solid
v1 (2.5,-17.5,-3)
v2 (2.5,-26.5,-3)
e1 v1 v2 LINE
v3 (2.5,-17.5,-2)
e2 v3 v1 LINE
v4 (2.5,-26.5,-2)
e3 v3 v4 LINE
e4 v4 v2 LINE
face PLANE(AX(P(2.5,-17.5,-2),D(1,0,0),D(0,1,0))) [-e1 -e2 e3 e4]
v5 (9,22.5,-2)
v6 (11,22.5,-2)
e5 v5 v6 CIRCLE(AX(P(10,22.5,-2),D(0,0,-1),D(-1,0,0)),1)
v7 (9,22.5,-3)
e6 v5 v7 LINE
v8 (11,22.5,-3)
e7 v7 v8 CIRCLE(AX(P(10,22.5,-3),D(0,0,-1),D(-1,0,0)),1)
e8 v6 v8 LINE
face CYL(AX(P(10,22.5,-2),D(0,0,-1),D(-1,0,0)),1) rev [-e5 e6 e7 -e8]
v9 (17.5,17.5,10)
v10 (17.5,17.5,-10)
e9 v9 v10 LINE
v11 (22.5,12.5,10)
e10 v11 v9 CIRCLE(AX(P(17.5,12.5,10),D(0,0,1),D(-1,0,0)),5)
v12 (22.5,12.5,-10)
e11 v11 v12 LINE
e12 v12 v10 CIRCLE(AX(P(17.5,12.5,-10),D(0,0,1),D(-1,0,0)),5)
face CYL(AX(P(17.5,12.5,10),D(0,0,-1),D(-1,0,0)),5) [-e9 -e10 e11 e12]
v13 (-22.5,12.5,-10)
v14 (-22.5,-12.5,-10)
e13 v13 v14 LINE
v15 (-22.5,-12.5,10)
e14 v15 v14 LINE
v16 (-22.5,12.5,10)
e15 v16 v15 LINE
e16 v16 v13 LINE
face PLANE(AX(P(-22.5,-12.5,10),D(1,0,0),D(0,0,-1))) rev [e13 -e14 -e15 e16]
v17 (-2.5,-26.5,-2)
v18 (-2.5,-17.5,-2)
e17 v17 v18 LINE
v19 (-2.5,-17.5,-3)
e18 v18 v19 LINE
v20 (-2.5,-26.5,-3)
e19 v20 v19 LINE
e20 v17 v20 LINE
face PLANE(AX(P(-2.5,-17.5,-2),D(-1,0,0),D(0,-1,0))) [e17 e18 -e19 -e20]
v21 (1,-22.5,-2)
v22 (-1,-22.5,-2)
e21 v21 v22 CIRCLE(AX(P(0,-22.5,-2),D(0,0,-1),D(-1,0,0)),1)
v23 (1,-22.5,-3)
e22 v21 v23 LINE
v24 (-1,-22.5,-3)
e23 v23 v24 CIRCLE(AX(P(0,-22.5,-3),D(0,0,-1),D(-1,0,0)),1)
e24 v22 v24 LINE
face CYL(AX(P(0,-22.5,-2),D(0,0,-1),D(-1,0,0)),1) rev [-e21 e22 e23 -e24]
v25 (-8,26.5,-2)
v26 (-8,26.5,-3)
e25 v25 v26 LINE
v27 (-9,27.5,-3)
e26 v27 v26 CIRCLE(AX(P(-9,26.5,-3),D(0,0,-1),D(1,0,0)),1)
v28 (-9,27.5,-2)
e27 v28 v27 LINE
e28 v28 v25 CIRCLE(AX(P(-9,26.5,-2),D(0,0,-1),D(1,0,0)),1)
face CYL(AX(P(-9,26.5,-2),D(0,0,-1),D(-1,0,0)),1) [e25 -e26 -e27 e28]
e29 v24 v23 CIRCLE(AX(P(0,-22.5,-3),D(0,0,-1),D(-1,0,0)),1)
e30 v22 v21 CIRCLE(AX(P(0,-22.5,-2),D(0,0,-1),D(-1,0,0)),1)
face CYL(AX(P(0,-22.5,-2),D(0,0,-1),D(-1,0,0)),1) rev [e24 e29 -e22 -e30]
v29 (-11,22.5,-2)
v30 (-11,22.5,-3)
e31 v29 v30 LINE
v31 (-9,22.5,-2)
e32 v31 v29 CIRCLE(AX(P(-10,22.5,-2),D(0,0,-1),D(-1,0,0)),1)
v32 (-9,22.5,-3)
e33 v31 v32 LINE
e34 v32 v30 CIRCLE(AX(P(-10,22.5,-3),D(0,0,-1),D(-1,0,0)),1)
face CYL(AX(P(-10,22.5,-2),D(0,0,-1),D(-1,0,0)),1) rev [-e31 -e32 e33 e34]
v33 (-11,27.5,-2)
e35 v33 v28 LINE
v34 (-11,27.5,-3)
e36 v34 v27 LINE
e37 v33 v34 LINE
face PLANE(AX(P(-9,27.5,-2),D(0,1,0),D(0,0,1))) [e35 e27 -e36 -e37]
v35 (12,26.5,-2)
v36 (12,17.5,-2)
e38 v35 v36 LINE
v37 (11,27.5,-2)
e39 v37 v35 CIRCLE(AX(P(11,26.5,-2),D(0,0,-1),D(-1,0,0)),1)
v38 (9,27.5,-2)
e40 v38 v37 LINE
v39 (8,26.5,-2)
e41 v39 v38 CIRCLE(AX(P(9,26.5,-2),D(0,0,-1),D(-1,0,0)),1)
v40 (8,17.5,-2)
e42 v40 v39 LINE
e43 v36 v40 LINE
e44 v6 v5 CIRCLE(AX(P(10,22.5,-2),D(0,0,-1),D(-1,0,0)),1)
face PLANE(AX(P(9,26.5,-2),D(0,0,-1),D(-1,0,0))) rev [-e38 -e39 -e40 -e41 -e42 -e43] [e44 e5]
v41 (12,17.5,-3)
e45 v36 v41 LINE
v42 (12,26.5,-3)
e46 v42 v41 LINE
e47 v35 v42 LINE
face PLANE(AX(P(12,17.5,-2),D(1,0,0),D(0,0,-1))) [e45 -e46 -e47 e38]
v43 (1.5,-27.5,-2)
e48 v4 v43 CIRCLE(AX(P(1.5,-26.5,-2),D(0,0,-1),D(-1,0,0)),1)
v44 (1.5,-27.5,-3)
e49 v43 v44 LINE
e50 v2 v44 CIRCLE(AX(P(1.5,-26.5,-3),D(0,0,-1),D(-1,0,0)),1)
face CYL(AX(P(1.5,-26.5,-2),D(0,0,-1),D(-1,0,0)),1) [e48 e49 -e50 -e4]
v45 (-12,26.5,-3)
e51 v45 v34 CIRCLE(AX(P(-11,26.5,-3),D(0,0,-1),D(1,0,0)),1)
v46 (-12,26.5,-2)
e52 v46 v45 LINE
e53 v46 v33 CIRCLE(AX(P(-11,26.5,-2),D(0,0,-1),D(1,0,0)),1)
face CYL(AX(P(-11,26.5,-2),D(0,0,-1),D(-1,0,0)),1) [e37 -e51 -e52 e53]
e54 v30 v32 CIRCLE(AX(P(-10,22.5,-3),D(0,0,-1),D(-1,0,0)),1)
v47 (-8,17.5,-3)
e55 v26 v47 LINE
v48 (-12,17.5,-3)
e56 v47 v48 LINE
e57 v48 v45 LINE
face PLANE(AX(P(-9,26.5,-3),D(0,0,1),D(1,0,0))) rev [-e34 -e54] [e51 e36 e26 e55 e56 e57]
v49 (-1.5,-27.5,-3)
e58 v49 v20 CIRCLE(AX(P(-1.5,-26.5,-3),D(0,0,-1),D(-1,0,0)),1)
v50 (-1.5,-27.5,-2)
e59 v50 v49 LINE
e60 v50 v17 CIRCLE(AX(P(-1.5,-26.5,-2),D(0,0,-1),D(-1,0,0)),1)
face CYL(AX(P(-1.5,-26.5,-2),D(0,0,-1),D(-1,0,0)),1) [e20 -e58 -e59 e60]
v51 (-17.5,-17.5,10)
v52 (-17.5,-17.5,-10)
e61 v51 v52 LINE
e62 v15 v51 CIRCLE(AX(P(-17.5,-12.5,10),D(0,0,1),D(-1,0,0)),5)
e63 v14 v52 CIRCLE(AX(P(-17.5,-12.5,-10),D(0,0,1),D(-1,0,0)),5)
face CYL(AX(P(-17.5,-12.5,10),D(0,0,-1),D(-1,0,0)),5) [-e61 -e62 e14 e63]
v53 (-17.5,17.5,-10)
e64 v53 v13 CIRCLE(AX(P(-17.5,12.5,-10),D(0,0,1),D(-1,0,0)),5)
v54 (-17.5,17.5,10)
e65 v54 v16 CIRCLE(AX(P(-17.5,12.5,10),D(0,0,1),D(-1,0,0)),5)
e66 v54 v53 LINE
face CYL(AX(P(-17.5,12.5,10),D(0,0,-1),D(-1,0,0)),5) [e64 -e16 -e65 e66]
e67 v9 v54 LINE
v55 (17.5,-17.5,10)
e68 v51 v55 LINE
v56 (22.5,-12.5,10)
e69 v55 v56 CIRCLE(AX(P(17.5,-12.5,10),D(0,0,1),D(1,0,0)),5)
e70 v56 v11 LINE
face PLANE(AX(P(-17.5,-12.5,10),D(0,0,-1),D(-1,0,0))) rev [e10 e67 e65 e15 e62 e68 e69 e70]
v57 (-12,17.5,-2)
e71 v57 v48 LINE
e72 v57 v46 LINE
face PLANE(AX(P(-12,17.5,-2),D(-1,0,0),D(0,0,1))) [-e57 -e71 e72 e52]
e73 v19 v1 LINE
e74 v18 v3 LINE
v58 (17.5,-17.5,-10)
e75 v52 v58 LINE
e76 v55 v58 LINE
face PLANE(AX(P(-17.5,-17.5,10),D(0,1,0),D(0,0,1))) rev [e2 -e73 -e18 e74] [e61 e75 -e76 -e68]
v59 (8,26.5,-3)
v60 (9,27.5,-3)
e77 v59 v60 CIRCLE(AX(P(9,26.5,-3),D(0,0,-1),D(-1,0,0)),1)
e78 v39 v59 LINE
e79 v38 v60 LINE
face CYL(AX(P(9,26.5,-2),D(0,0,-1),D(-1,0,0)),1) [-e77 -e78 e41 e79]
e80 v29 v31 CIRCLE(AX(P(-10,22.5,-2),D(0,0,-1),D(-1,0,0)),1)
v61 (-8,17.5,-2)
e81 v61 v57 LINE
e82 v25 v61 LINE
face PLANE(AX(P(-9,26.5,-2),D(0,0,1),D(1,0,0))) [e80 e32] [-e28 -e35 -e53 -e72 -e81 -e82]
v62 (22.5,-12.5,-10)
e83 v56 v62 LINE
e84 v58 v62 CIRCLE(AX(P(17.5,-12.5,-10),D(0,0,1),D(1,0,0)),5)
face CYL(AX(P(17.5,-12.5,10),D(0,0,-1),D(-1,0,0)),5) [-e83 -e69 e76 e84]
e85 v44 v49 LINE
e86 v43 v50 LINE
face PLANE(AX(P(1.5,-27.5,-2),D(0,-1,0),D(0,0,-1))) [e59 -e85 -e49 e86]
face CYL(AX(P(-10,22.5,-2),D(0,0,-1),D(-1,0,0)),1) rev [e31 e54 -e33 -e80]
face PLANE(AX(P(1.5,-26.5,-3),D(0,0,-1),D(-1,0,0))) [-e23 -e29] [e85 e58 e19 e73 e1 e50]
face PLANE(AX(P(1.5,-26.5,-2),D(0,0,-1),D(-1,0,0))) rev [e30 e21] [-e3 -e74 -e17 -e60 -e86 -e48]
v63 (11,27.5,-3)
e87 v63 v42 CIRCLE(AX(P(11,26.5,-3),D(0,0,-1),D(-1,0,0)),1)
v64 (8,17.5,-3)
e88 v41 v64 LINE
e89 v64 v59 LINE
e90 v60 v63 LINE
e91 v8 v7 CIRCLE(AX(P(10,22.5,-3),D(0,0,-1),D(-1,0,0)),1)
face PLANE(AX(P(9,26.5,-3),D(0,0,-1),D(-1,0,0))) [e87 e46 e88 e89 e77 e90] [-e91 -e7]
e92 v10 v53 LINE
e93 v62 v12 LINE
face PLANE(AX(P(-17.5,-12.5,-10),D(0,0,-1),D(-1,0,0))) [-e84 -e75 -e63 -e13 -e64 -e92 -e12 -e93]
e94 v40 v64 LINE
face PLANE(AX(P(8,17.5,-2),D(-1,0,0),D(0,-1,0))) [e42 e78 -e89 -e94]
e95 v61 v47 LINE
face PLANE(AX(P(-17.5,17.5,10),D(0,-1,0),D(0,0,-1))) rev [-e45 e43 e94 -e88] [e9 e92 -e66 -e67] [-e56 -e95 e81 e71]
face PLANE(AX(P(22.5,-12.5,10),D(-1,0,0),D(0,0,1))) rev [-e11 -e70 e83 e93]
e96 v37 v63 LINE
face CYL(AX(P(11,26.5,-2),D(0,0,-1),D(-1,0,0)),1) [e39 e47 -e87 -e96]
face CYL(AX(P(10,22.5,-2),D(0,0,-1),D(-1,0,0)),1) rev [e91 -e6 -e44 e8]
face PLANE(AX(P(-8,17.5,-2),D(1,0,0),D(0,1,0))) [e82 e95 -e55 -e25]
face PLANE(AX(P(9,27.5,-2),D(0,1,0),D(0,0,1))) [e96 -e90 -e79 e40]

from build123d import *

# Parameters (mm, degrees)
BOSS_EXTRUDE1_DEPTH = 10
SKETCH3_R           = 1
BOSS_EXTRUDE2_DEPTH = 1
SKETCH4_R           = 1
CUT_EXTRUDE1_DEPTH  = 1


with BuildPart() as part:
    # Sketch1 → Boss-Extrude1 (new, symmetric)
    with BuildSketch(Plane.XY):
        with BuildLine():
            Line((-17.5, -17.5), (17.5, -17.5))
            ThreePointArc((17.5, -17.5), (21.035533906, -16.035533906), (22.5, -12.5))
            Line((22.5, -12.5), (22.5, 12.5))
            ThreePointArc((22.5, 12.5), (21.035533906, 16.035533906), (17.5, 17.5))
            Line((17.5, 17.5), (-17.5, 17.5))
            ThreePointArc((-17.5, 17.5), (-21.035533906, 16.035533906), (-22.5, 12.5))
            Line((-22.5, 12.5), (-22.5, -12.5))
            ThreePointArc((-22.5, -12.5), (-21.035533906, -16.035533906), (-17.5, -17.5))
        make_face()
    extrude(amount=BOSS_EXTRUDE1_DEPTH, both=True)

    # Sketch3 → Boss-Extrude2 (add)
    # profile 1 of 3: a face of its own
    with BuildSketch(Plane(origin=(0, 0, -3), x_dir=(-1, 0, 0), z_dir=(0, 0, -1))):
        with BuildLine():
            Line((-8, 17.5), (-12, 17.5))
            Line((-12, 17.5), (-12, 26.5))
            ThreePointArc((-12, 26.5), (-11.707106781, 27.207106781), (-11, 27.5))
            Line((-11, 27.5), (-9, 27.5))
            ThreePointArc((-9, 27.5), (-8.292893219, 27.207106781), (-8, 26.5))
            Line((-8, 26.5), (-8, 17.5))
        make_face()
    # profile 2 of 3: a face of its own
    with BuildSketch(Plane(origin=(0, 0, -3), x_dir=(-1, 0, 0), z_dir=(0, 0, -1))):
        with BuildLine():
            Line((8, 17.5), (12, 17.5))
            Line((12, 17.5), (12, 26.5))
            ThreePointArc((12, 26.5), (11.707106781, 27.207106781), (11, 27.5))
            Line((11, 27.5), (9, 27.5))
            ThreePointArc((9, 27.5), (8.292893219, 27.207106781), (8, 26.5))
            Line((8, 26.5), (8, 17.5))
        make_face()
    # profile 3 of 3: a face of its own
    with BuildSketch(Plane(origin=(0, 0, -3), x_dir=(-1, 0, 0), z_dir=(0, 0, -1))):
        with BuildLine():
            Line((-2.5, -17.5), (2.5, -17.5))
            Line((2.5, -17.5), (2.5, -26.5))
            ThreePointArc((2.5, -26.5), (2.207106781, -27.207106781), (1.5, -27.5))
            Line((1.5, -27.5), (-1.5, -27.5))
            ThreePointArc((-1.5, -27.5), (-2.207106781, -27.207106781), (-2.5, -26.5))
            Line((-2.5, -26.5), (-2.5, -17.5))
        make_face()
        with Locations((0, -22.5)):
            Circle(SKETCH3_R, mode=Mode.SUBTRACT)
    extrude(amount=-BOSS_EXTRUDE2_DEPTH)

    # Sketch4 → Cut-Extrude1 (cut)
    with BuildSketch(Plane(origin=(0, 0, -3), x_dir=(-1, 0, 0), z_dir=(0, 0, -1))):
        with Locations((-10, 22.5)):
            Circle(SKETCH4_R)
        with Locations((10, 22.5)):
            Circle(SKETCH4_R)
    extrude(amount=-CUT_EXTRUDE1_DEPTH, mode=Mode.SUBTRACT)


solid = part.part
